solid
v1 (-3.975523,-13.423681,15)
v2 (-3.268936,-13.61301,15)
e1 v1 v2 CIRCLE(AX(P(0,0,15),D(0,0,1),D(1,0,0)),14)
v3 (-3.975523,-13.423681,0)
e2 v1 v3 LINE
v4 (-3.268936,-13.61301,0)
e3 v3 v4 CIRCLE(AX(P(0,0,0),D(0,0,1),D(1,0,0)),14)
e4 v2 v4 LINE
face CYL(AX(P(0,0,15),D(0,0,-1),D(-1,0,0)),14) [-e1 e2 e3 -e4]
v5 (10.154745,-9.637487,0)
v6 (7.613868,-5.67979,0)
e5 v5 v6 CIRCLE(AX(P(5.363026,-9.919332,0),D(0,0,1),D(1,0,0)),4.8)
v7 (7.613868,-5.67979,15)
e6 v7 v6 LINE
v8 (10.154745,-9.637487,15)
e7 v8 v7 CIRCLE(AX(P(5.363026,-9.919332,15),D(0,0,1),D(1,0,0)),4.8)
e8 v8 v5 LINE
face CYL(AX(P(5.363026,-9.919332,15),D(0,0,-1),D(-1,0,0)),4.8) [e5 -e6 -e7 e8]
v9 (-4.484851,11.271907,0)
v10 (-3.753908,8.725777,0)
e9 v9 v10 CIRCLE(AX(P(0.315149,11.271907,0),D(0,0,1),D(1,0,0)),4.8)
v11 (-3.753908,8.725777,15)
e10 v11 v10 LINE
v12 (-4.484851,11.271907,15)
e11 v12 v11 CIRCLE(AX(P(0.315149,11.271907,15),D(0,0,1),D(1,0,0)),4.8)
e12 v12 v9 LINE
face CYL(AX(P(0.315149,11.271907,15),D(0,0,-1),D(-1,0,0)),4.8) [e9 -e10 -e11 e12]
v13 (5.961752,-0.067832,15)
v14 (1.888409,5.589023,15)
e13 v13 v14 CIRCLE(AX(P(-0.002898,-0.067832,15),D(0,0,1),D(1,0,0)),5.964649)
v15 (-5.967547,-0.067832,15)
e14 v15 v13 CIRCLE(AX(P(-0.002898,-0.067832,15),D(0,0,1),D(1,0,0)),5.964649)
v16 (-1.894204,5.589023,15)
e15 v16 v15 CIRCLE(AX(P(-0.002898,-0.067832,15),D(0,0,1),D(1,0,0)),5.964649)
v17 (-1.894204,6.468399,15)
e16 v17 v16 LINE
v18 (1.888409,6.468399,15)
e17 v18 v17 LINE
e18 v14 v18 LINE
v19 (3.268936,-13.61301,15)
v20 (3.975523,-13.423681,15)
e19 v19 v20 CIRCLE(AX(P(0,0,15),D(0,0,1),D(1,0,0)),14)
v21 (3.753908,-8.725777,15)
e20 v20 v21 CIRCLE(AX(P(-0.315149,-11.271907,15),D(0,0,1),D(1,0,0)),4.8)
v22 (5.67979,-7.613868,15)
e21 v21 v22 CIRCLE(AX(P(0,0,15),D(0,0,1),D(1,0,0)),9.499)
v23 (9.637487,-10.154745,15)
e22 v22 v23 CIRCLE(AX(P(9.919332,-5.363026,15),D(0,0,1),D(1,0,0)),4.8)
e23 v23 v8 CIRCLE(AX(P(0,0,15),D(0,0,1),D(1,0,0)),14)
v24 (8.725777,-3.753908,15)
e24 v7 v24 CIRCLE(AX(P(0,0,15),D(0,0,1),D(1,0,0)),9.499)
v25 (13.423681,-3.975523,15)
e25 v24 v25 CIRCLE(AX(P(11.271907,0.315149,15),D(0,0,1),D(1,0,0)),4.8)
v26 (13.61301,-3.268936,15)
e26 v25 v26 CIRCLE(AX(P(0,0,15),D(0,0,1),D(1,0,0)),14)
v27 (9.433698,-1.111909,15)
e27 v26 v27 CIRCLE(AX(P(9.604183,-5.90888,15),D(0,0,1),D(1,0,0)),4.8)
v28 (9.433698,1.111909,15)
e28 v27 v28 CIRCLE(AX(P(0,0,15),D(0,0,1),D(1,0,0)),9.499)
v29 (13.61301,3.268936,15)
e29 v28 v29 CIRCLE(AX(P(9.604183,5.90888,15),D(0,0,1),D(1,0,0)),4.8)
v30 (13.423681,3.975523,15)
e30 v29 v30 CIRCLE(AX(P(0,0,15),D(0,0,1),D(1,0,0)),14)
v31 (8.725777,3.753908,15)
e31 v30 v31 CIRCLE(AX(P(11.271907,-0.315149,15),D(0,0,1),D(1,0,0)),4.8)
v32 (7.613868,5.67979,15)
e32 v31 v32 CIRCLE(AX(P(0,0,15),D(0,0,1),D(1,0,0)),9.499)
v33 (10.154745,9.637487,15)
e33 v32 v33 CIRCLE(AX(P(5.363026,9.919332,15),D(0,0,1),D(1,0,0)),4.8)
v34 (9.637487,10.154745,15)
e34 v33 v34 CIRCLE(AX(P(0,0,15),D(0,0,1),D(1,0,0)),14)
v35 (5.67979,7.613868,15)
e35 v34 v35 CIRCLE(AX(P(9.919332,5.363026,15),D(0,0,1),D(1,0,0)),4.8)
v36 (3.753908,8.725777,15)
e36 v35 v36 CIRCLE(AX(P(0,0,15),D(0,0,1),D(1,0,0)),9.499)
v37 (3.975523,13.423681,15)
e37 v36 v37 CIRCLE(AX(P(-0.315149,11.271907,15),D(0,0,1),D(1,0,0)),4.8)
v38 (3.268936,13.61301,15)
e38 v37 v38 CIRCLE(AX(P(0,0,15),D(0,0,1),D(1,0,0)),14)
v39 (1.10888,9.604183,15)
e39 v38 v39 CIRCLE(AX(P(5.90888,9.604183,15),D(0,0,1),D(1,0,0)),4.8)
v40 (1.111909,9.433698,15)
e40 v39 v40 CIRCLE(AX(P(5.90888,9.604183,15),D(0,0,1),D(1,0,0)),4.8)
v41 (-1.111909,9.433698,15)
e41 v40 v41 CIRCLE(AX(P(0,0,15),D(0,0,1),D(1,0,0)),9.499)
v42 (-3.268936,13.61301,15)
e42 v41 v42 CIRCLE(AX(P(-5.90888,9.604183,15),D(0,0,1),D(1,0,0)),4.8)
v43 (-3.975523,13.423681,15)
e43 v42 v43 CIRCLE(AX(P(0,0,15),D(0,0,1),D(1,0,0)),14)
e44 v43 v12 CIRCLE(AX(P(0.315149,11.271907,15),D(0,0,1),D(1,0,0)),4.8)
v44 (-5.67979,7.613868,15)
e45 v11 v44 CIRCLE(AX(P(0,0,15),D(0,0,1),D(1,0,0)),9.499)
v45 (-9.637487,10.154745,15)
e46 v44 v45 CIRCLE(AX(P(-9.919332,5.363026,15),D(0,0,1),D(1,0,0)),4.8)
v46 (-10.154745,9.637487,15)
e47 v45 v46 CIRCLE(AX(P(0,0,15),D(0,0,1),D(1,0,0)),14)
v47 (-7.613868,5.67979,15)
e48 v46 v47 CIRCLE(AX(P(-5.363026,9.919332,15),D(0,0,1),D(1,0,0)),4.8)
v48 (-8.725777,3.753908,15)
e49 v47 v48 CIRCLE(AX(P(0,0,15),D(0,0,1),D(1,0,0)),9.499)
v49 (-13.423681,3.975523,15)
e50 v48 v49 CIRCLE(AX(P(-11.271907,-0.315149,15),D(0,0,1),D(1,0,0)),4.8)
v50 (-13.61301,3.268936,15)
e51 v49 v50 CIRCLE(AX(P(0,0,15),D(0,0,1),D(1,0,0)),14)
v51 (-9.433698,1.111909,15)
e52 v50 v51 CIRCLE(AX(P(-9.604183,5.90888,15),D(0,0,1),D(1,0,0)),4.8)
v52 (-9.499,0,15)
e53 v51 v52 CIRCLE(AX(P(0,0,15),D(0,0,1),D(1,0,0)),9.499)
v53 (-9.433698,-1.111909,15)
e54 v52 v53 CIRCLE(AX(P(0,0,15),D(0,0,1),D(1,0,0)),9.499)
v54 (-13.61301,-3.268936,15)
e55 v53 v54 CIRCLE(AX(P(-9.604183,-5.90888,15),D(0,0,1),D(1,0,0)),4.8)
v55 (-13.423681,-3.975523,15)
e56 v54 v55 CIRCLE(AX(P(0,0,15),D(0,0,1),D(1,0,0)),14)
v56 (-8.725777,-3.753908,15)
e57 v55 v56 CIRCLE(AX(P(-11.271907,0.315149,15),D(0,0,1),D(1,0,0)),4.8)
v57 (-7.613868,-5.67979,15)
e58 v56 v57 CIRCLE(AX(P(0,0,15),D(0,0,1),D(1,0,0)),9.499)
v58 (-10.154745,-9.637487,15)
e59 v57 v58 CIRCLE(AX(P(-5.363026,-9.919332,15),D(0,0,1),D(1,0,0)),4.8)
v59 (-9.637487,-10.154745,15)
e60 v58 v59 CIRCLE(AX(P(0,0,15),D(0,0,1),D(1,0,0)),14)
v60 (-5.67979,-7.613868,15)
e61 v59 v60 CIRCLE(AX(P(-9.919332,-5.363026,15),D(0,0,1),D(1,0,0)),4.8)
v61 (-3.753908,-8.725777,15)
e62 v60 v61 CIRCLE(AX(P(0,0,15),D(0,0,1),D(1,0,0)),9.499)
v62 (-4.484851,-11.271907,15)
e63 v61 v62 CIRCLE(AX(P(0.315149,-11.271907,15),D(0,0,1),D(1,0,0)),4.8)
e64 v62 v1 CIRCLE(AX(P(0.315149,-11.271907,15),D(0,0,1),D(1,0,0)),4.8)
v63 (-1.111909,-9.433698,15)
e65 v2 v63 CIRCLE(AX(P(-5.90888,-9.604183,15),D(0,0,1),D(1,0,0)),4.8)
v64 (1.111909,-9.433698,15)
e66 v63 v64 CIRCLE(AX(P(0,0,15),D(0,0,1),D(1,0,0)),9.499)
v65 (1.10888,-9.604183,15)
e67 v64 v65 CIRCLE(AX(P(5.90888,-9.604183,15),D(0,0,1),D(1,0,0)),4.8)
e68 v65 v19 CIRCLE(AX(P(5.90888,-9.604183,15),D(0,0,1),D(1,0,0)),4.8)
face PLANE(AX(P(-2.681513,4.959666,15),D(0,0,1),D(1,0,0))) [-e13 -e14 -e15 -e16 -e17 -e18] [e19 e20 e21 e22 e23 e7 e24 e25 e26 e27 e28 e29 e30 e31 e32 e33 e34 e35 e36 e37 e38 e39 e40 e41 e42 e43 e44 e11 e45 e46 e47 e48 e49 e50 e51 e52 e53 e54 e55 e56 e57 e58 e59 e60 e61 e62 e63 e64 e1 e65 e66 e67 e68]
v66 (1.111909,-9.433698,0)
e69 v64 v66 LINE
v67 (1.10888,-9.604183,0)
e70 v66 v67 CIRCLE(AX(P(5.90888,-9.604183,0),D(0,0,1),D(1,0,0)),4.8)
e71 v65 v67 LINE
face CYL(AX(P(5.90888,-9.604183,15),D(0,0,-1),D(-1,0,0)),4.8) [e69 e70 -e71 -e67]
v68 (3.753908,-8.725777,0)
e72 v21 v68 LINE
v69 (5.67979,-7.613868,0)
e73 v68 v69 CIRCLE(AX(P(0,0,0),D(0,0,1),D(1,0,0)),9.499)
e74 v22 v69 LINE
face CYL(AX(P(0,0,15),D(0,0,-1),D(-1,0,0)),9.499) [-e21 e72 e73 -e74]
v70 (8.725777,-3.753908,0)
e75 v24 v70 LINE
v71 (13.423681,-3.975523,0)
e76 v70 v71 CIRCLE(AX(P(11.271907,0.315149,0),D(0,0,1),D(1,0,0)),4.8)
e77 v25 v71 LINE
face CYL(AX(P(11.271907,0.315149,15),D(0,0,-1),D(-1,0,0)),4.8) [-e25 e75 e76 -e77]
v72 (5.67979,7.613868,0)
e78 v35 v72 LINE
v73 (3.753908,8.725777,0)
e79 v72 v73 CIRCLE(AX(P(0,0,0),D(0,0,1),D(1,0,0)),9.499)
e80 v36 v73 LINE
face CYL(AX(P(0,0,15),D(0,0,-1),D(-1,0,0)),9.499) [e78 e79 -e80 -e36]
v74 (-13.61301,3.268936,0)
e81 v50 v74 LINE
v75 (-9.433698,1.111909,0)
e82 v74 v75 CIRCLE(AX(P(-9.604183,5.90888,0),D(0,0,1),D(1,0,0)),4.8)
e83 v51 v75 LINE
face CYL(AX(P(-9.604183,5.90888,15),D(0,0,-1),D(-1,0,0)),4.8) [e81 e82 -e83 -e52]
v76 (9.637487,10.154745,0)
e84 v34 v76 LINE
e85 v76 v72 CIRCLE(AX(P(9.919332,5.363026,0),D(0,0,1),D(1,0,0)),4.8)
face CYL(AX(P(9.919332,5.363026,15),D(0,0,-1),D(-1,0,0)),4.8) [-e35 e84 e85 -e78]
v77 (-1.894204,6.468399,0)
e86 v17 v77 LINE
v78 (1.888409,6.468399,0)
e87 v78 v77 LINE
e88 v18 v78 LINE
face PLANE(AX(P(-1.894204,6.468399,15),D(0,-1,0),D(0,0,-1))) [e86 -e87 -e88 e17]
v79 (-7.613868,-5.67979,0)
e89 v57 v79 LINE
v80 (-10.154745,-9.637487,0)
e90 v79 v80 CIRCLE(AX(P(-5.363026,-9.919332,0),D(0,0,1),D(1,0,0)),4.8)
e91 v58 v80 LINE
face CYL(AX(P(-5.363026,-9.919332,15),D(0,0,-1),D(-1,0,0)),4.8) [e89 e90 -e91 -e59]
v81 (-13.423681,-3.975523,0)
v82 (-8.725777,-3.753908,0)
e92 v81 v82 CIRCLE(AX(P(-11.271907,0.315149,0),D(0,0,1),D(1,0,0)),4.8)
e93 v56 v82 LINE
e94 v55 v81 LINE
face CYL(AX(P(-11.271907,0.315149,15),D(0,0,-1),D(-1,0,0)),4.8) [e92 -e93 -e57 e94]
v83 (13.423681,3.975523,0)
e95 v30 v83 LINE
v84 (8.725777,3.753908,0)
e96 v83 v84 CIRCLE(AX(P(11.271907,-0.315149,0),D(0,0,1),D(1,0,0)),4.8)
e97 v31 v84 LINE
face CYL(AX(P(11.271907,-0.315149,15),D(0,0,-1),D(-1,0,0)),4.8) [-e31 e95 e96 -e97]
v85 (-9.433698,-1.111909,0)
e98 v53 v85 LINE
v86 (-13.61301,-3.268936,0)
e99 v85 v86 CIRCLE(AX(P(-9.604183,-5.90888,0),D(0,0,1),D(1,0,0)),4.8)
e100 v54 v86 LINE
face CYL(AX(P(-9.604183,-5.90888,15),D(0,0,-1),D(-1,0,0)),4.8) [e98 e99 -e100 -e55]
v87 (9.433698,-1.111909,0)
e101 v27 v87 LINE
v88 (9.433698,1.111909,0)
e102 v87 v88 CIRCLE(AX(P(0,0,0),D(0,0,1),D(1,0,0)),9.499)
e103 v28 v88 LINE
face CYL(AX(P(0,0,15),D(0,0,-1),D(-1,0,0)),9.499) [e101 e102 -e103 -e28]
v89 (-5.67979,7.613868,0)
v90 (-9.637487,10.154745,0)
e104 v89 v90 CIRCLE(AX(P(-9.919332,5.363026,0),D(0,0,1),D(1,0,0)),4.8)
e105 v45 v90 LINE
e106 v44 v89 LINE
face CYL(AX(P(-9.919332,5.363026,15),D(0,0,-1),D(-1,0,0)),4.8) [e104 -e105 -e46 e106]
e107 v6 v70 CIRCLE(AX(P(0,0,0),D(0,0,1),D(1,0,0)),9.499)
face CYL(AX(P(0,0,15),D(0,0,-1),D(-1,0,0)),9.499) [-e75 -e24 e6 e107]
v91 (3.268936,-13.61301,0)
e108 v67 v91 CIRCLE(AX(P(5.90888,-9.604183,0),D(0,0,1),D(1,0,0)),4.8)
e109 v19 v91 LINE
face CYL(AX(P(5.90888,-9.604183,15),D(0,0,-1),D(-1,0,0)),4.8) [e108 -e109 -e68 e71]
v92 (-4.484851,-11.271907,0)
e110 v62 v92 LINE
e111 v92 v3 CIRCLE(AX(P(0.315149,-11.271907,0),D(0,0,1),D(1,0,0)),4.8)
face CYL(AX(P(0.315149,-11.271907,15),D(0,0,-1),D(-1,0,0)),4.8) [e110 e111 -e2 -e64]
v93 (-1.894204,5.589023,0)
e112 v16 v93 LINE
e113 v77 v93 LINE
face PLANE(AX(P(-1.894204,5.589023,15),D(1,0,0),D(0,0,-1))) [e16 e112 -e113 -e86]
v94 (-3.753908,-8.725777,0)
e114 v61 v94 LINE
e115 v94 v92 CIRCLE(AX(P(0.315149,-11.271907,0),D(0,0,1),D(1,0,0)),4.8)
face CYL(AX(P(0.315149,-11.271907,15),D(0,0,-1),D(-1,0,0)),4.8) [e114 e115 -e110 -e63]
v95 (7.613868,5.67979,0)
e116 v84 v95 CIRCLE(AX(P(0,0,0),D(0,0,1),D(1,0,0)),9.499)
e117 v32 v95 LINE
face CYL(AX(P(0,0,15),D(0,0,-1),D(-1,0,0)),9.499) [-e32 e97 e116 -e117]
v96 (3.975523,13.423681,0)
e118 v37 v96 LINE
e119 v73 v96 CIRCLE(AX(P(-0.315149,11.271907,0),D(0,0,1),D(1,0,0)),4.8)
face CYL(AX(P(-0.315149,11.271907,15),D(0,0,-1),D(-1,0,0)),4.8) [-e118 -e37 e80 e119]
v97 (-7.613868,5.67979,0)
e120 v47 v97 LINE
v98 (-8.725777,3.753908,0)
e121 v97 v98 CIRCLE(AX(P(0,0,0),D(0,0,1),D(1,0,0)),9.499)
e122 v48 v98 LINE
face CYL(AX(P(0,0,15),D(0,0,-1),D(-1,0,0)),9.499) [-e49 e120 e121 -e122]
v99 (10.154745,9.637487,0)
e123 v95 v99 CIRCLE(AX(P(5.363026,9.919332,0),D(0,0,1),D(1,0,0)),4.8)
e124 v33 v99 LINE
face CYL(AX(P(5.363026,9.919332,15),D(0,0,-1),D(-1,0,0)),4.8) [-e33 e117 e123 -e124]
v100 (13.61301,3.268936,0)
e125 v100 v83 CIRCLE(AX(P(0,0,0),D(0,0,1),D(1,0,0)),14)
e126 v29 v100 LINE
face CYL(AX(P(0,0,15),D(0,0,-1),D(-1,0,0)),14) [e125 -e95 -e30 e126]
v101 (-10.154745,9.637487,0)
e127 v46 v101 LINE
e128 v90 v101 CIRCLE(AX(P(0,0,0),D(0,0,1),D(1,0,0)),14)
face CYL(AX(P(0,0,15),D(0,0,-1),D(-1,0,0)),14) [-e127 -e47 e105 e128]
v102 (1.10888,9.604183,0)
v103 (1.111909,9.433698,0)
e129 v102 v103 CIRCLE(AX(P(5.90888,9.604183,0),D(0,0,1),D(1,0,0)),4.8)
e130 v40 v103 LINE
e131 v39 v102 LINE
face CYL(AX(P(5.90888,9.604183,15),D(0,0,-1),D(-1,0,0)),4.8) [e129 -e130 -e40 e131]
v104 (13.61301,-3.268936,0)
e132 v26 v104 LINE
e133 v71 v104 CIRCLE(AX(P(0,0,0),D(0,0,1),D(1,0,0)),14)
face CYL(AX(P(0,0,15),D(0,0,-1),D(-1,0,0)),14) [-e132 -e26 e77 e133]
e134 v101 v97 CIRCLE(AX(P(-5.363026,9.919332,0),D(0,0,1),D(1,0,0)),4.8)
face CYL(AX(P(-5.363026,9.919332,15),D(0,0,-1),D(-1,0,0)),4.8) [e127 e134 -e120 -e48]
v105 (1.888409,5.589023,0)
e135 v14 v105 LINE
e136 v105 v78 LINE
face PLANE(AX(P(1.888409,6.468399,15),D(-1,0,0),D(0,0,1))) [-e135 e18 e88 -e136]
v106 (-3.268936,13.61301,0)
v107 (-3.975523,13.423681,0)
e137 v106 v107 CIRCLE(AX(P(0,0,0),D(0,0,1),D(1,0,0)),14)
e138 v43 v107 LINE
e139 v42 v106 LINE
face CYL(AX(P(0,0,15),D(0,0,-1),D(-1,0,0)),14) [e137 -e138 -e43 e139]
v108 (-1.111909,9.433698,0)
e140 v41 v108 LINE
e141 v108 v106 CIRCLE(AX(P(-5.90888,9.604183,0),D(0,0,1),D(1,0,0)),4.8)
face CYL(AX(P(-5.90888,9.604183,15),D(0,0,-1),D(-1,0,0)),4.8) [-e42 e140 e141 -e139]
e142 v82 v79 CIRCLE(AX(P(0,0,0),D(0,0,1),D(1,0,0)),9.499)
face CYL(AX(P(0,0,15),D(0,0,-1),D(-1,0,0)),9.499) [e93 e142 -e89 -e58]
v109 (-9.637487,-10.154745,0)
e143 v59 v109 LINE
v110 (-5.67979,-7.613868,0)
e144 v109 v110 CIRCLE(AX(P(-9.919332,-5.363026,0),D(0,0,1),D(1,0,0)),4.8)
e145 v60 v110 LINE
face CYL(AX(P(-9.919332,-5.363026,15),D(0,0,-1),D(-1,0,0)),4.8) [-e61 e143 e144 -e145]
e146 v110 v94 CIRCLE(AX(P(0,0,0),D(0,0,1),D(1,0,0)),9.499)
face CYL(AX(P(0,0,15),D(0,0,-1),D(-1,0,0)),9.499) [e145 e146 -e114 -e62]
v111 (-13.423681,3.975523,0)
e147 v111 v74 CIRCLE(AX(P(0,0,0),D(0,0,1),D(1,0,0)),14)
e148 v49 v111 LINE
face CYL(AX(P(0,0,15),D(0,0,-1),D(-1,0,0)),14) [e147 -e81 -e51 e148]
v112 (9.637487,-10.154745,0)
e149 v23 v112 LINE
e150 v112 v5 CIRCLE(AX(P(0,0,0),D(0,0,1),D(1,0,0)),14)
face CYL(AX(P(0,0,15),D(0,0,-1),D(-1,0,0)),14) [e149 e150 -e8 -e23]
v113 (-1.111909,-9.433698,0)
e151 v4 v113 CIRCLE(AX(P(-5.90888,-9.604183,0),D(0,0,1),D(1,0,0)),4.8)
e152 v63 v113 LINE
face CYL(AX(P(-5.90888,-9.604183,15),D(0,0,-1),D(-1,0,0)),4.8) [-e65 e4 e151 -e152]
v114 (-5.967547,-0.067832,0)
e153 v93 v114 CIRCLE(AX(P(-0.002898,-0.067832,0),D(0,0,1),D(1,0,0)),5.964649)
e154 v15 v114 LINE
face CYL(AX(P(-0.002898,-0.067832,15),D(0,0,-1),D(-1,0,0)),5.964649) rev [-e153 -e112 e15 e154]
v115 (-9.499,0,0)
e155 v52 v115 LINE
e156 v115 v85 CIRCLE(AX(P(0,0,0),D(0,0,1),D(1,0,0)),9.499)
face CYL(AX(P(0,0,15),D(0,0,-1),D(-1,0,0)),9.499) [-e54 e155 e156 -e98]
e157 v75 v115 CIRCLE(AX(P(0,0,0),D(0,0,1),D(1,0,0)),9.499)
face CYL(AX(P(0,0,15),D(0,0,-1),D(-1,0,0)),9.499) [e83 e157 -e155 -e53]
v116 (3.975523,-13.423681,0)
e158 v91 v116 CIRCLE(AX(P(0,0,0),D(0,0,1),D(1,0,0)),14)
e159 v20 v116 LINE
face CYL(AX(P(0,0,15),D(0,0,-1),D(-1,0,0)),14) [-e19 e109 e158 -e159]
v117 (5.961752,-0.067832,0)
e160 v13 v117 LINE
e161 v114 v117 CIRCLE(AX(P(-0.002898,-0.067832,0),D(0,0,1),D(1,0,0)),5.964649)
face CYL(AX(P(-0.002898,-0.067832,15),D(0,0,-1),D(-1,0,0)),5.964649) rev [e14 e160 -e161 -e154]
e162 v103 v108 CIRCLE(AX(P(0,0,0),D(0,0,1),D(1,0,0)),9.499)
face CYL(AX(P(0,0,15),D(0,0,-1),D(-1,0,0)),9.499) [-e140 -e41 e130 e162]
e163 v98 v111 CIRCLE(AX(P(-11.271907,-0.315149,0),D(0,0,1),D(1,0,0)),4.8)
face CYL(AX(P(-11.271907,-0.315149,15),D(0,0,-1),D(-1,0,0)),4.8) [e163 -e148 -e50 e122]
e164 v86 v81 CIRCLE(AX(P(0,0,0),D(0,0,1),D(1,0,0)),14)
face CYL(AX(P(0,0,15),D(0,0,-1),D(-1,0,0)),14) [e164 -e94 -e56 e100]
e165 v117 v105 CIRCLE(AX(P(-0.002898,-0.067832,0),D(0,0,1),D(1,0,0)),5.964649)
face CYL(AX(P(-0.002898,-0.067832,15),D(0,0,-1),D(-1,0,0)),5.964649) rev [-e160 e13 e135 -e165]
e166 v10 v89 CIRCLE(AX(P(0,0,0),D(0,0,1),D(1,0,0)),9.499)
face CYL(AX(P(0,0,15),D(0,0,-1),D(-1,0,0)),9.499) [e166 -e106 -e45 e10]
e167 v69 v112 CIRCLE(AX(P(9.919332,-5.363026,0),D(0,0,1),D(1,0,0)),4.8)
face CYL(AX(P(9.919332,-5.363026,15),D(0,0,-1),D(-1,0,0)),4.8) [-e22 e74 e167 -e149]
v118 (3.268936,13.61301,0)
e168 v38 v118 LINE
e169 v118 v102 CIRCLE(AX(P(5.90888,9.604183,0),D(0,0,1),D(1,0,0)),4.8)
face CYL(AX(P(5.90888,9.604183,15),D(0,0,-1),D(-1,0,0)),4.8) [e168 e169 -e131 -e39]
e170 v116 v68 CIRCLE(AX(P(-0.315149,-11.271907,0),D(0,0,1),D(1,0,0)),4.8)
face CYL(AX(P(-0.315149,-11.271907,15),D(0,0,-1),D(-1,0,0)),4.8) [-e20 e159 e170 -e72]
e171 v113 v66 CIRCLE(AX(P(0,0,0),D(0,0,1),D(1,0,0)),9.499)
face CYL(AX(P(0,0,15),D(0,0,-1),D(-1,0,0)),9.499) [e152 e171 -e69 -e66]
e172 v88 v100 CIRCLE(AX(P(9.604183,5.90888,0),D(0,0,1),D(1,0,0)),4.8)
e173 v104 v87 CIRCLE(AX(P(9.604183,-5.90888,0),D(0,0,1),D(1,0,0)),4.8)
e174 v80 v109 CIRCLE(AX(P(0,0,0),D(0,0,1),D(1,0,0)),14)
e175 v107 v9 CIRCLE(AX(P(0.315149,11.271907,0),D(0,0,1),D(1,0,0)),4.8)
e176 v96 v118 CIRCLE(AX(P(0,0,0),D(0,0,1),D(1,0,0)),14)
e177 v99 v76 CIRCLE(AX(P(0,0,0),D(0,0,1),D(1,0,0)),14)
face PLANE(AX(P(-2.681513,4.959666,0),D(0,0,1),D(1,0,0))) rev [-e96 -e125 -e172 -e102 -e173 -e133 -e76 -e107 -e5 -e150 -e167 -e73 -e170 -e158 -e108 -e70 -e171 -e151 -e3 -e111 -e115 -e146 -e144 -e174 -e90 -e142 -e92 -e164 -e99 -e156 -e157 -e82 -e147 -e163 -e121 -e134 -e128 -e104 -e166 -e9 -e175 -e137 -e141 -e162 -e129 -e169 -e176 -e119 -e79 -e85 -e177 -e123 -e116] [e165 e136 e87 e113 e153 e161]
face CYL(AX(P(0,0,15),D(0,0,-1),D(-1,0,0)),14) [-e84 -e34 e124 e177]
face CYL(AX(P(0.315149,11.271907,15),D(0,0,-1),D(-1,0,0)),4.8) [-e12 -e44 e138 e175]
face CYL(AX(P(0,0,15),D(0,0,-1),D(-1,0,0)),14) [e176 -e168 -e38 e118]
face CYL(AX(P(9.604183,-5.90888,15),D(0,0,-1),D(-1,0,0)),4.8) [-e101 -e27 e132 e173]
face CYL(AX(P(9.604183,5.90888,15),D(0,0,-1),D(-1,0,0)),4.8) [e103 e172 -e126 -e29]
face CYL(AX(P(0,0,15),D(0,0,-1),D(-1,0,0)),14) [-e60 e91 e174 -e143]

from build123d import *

# Parameters (mm, degrees)
EXTRUDE_1_DEPTH = 15


with BuildPart() as part:
    # 草图2 → 凸台-拉伸1 (new body)
    with BuildSketch(Plane.XY):
        with BuildLine():
            ThreePointArc((-10.154744655, 9.637487276), (-9.402240771, 7.326120193), (-7.613867765, 5.67979037))
            ThreePointArc((-7.613867765, 5.67979037), (-8.226375311, 4.7495), (-8.725776632, 3.753907721))
            ThreePointArc((-8.725776632, 3.753907721), (-11.045726583, 4.479519264), (-13.423681137, 3.975523202))
            ThreePointArc((-13.423681137, 3.975523202), (-13.522961568, 3.623466631), (-13.613010478, 3.268936482))
            ThreePointArc((-13.613010478, 3.268936482), (-11.805639456, 1.643485813), (-9.433698091, 1.111908866))
            ThreePointArc((-9.433698091, 1.111908866), (-9.499, 0), (-9.433698091, -1.111908866))
            ThreePointArc((-9.433698091, -1.111908866), (-11.805639456, -1.643485813), (-13.613010478, -3.268936482))
            ThreePointArc((-13.613010478, -3.268936482), (-13.522961568, -3.623466631), (-13.423681137, -3.975523202))
            ThreePointArc((-13.423681137, -3.975523202), (-11.045726583, -4.479519264), (-8.725776632, -3.753907721))
            ThreePointArc((-8.725776632, -3.753907721), (-8.226375311, -4.7495), (-7.613867765, -5.67979037))
            ThreePointArc((-7.613867765, -5.67979037), (-9.402240771, -7.326120193), (-10.154744655, -9.637487276))
            ThreePointArc((-10.154744655, -9.637487276), (-9.899494937, -9.899494937), (-9.637487276, -10.154744655))
            ThreePointArc((-9.637487276, -10.154744655), (-7.326120193, -9.402240771), (-5.67979037, -7.613867765))
            ThreePointArc((-5.67979037, -7.613867765), (-4.7495, -8.226375311), (-3.753907721, -8.725776632))
            ThreePointArc((-3.753907721, -8.725776632), (-4.479519264, -11.045726583), (-3.975523202, -13.423681137))
            ThreePointArc((-3.975523202, -13.423681137), (-3.623466631, -13.522961568), (-3.268936482, -13.613010478))
            ThreePointArc((-3.268936482, -13.613010478), (-1.643485813, -11.805639456), (-1.111908866, -9.433698091))
            ThreePointArc((-1.111908866, -9.433698091), (0, -9.499), (1.111908866, -9.433698091))
            ThreePointArc((1.111908866, -9.433698091), (1.643485813, -11.805639456), (3.268936482, -13.613010478))
            ThreePointArc((3.268936482, -13.613010478), (3.623466631, -13.522961568), (3.975523202, -13.423681137))
            ThreePointArc((3.975523202, -13.423681137), (4.479519264, -11.045726583), (3.753907721, -8.725776632))
            ThreePointArc((3.753907721, -8.725776632), (4.7495, -8.226375311), (5.67979037, -7.613867765))
            ThreePointArc((5.67979037, -7.613867765), (7.326120193, -9.402240771), (9.637487276, -10.154744655))
            ThreePointArc((9.637487276, -10.154744655), (9.899494937, -9.899494937), (10.154744655, -9.637487276))
            ThreePointArc((10.154744655, -9.637487276), (9.402240771, -7.326120193), (7.613867765, -5.67979037))
            ThreePointArc((7.613867765, -5.67979037), (8.226375311, -4.7495), (8.725776632, -3.753907721))
            ThreePointArc((8.725776632, -3.753907721), (11.045726583, -4.479519264), (13.423681137, -3.975523202))
            ThreePointArc((13.423681137, -3.975523202), (13.522961568, -3.623466631), (13.613010478, -3.268936482))
            ThreePointArc((13.613010478, -3.268936482), (11.805639456, -1.643485813), (9.433698091, -1.111908866))
            ThreePointArc((9.433698091, -1.111908866), (9.499, 0), (9.433698091, 1.111908866))
            ThreePointArc((9.433698091, 1.111908866), (11.805639456, 1.643485813), (13.613010478, 3.268936482))
            ThreePointArc((13.613010478, 3.268936482), (13.522961568, 3.623466631), (13.423681137, 3.975523202))
            ThreePointArc((13.423681137, 3.975523202), (11.045726583, 4.479519264), (8.725776632, 3.753907721))
            ThreePointArc((8.725776632, 3.753907721), (8.226375311, 4.7495), (7.613867765, 5.67979037))
            ThreePointArc((7.613867765, 5.67979037), (9.402240771, 7.326120193), (10.154744655, 9.637487276))
            ThreePointArc((10.154744655, 9.637487276), (9.899494937, 9.899494937), (9.637487276, 10.154744655))
            ThreePointArc((9.637487276, 10.154744655), (7.326120193, 9.402240771), (5.67979037, 7.613867765))
            ThreePointArc((5.67979037, 7.613867765), (4.7495, 8.226375311), (3.753907721, 8.725776632))
            ThreePointArc((3.753907721, 8.725776632), (4.479519264, 11.045726583), (3.975523202, 13.423681137))
            ThreePointArc((3.975523202, 13.423681137), (3.623466631, 13.522961568), (3.268936482, 13.613010478))
            ThreePointArc((3.268936482, 13.613010478), (1.643485813, 11.805639456), (1.111908866, 9.433698091))
            ThreePointArc((1.111908866, 9.433698091), (0, 9.499), (-1.111908866, 9.433698091))
            ThreePointArc((-1.111908866, 9.433698091), (-1.643485813, 11.805639456), (-3.268936482, 13.613010478))
            ThreePointArc((-3.268936482, 13.613010478), (-3.623466631, 13.522961568), (-3.975523202, 13.423681137))
            ThreePointArc((-3.975523202, 13.423681137), (-4.479519264, 11.045726583), (-3.753907721, 8.725776632))
            ThreePointArc((-3.753907721, 8.725776632), (-4.7495, 8.226375311), (-5.67979037, 7.613867765))
            ThreePointArc((-5.67979037, 7.613867765), (-7.326120193, 9.402240771), (-9.637487276, 10.154744655))
            ThreePointArc((-9.637487276, 10.154744655), (-9.899494937, 9.899494937), (-10.154744655, 9.637487276))
        make_face()
        with BuildLine():
            Line((-1.894204479, 6.468399347), (1.888409216, 6.468399347))
            Line((1.888409216, 6.468399347), (1.888409216, 5.589022546))
            ThreePointArc((1.888409216, 5.589022546), (-0.002897631, -6.03248103), (-1.894204479, 5.589022546))
            Line((-1.894204479, 5.589022546), (-1.894204479, 6.468399347))
        make_face(mode=Mode.SUBTRACT)
    extrude(amount=EXTRUDE_1_DEPTH)


solid = part.part
